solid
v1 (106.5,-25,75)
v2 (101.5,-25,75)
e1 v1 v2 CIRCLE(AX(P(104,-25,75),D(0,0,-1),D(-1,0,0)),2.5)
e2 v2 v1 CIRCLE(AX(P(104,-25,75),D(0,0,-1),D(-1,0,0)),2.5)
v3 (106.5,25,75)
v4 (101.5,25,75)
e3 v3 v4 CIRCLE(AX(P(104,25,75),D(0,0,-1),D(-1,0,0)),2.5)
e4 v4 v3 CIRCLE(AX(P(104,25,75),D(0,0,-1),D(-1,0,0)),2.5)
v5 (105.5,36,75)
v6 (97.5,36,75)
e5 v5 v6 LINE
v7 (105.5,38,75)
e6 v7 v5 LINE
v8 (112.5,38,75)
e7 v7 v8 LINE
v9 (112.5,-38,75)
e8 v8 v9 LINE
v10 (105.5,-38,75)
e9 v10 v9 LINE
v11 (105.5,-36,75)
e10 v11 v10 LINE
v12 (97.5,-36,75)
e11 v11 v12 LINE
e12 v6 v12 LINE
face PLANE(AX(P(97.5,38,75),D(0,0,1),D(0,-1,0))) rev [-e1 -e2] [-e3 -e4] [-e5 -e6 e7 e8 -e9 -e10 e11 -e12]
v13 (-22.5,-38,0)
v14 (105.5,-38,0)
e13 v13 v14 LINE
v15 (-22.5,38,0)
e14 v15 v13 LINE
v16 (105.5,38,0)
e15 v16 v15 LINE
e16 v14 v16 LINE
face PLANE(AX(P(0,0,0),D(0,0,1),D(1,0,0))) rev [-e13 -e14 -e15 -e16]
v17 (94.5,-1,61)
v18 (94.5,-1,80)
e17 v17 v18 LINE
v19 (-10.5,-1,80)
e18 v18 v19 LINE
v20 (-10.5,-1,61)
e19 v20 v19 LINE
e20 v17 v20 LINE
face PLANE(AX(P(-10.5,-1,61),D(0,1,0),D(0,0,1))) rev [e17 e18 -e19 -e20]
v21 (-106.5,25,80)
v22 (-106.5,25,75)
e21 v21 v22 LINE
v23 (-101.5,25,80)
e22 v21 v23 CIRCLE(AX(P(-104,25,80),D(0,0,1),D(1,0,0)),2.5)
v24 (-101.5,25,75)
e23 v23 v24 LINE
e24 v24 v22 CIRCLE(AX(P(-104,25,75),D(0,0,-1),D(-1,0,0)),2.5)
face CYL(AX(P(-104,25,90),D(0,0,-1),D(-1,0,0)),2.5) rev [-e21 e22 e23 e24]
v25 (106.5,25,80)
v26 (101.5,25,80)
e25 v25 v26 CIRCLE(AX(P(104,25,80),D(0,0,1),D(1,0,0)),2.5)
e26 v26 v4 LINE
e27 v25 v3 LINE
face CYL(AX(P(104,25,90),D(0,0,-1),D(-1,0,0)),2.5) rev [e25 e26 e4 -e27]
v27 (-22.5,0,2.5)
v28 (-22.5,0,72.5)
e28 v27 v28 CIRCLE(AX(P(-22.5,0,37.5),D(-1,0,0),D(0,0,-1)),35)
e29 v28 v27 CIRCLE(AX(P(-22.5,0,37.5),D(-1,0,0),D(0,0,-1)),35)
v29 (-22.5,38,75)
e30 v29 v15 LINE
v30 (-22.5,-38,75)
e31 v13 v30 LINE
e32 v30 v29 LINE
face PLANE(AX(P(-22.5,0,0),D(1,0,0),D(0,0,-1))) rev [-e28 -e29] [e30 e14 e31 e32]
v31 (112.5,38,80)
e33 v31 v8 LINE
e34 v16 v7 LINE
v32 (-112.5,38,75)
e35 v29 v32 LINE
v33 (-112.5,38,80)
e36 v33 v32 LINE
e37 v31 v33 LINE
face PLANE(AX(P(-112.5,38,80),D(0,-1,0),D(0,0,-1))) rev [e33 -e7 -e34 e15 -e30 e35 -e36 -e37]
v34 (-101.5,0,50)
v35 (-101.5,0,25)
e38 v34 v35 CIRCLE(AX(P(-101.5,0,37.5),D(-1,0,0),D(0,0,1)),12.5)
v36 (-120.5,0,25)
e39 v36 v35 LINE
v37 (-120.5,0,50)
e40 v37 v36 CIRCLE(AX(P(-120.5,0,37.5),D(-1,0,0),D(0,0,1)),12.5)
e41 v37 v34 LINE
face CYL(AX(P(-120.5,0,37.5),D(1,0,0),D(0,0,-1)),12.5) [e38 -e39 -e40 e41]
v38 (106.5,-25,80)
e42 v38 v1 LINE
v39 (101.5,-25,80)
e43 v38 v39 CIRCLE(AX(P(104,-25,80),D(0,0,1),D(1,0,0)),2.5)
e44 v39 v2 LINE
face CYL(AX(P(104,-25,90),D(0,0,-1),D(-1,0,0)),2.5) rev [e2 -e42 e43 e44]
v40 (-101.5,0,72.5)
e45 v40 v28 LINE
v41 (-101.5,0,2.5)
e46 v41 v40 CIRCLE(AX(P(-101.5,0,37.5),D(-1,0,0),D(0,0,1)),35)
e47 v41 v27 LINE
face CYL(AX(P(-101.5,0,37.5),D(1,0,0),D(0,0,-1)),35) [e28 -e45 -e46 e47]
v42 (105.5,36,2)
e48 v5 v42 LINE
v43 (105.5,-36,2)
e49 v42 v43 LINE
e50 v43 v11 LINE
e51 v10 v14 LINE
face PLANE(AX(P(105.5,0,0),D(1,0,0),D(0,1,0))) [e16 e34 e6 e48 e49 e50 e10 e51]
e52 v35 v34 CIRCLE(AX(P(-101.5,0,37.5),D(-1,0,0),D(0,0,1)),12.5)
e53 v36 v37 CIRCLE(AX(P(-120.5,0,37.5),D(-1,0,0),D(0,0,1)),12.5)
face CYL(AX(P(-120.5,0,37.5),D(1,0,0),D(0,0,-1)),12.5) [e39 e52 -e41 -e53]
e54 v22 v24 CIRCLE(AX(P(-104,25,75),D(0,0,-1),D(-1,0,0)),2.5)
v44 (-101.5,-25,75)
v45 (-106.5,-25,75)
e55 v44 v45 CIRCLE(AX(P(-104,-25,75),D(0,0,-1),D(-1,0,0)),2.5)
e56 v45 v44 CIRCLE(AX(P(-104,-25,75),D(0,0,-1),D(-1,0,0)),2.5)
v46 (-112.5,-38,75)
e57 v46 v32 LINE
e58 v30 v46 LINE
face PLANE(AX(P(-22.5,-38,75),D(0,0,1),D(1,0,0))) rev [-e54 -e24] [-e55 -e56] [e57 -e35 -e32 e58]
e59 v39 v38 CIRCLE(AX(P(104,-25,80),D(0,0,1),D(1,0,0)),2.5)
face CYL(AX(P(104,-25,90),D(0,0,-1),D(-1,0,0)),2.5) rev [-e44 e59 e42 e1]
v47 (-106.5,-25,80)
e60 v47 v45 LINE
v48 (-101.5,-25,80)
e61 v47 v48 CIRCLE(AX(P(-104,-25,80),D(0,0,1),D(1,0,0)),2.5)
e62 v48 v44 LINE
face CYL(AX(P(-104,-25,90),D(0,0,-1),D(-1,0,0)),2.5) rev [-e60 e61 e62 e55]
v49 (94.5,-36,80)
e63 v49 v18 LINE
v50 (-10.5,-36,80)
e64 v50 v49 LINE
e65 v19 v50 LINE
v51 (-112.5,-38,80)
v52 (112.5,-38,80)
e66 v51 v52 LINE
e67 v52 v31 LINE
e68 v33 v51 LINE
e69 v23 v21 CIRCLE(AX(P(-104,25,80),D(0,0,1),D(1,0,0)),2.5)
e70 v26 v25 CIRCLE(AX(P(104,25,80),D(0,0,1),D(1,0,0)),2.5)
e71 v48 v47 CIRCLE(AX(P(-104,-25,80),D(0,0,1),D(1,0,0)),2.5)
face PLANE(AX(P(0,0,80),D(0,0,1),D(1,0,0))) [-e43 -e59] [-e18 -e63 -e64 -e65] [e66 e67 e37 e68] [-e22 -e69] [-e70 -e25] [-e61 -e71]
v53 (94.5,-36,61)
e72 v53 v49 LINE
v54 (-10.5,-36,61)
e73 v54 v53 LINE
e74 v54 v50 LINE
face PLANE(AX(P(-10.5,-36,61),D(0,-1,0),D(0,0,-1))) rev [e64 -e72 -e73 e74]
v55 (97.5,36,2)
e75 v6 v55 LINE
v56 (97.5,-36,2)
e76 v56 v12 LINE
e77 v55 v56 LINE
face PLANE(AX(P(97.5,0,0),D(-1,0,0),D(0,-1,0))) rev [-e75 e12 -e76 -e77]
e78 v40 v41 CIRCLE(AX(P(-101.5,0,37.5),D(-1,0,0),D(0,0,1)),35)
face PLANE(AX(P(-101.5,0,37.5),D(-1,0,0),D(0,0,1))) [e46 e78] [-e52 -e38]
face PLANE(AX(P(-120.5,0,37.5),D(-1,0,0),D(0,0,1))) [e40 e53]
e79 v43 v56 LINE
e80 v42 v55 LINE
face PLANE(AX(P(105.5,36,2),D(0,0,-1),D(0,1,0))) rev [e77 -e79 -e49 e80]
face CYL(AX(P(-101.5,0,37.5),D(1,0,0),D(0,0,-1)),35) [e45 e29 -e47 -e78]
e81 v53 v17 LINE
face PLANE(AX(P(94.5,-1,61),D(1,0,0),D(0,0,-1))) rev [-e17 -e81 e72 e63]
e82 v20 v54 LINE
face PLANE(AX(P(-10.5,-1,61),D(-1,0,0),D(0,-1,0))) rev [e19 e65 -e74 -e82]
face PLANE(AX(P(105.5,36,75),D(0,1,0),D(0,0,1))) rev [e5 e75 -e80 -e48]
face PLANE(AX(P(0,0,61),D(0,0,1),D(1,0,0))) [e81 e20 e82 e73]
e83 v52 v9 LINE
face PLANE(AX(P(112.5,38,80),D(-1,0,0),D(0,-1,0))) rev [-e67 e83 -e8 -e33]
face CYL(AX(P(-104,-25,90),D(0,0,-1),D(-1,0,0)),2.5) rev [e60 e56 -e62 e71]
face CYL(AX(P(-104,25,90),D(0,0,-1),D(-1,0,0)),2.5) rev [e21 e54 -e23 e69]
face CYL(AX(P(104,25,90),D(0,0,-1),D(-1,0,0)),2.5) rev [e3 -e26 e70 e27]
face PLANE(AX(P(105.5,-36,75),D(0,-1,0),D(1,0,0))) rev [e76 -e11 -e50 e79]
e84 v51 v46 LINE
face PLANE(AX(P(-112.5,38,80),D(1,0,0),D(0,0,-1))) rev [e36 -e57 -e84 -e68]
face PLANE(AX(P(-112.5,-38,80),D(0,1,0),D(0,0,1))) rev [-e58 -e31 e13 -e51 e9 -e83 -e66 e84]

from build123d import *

# Parameters (mm, degrees)
SKETCH_1_W          = 225
SKETCH_1_H          = 76
EXTRUDE_1_DEPTH     = 80
SKETCH_2_W          = 75
SKETCH_2_H          = 76
CUT_EXTRUDE_1_DEPTH = 90
SKETCH_3_W          = 75
SKETCH_3_H          = 76
CUT_EXTRUDE_2_DEPTH = 15
SKETCH_4_R          = 2.5
CUT_EXTRUDE_3_DEPTH = 15
SKETCH_5_R          = 35
EXTRUDE_2_DEPTH     = 79
SKETCH_6_R          = 12.5
EXTRUDE_3_DEPTH     = 19
SKETCH_7_W          = 105
SKETCH_7_H          = 35
CUT_EXTRUDE_4_DEPTH = 19
EXTRUDE_4_DEPTH     = 8


with BuildPart() as part:
    # 草图1 → 凸台-拉伸1 (new body)
    with BuildSketch(Plane.XY):
        Rectangle(SKETCH_1_W, SKETCH_1_H)
    extrude(amount=EXTRUDE_1_DEPTH)

    # 草图2 → 切除-拉伸1 (cut)
    with BuildSketch(Plane.ZY.offset(112.5)):
        with Locations((37.5, 0)):
            Rectangle(SKETCH_2_W, SKETCH_2_H)
    extrude(amount=-CUT_EXTRUDE_1_DEPTH, mode=Mode.SUBTRACT)

    # 草图3 → 切除-拉伸2 (cut)
    with BuildSketch(Plane(origin=(112.5, 0, 0), x_dir=(0, 0, -1), z_dir=(1, 0, 0))):
        with Locations((-37.5, 0)):
            Rectangle(SKETCH_3_W, SKETCH_3_H)
    extrude(amount=-CUT_EXTRUDE_2_DEPTH, mode=Mode.SUBTRACT)

    # 草图4 → 切除-拉伸3 (cut)
    with BuildSketch(Plane(origin=(0, 0, 75), x_dir=(-1, 0, 0), z_dir=(0, 0, -1))):
        with Locations((104, -25)):
            Circle(SKETCH_4_R)
        with Locations((104, 25)):
            Circle(SKETCH_4_R)
        with Locations((-104, -25)):
            Circle(SKETCH_4_R)
        with Locations((-104, 25)):
            Circle(SKETCH_4_R)
    extrude(amount=-CUT_EXTRUDE_3_DEPTH, mode=Mode.SUBTRACT)

    # 草图5 → 凸台-拉伸2 (add)
    with BuildSketch(Plane.ZY.offset(22.5)):
        with Locations(Location((37.5, 0, 0), (0, 0, 180))):
            Circle(SKETCH_5_R)
    extrude(amount=EXTRUDE_2_DEPTH)

    # 草图6 → 凸台-拉伸3 (add)
    with BuildSketch(Plane.ZY.offset(101.5)):
        with Locations((37.5, 0)):
            Circle(SKETCH_6_R)
    extrude(amount=EXTRUDE_3_DEPTH)

    # 草图7 → 切除-拉伸4 (cut)
    with BuildSketch(Plane.XY.offset(80)):
        with Locations((42, -18.5)):
            Rectangle(SKETCH_7_W, SKETCH_7_H)
    extrude(amount=-CUT_EXTRUDE_4_DEPTH, mode=Mode.SUBTRACT)

    # 草图8 → 凸台-拉伸4 (add)
    with BuildSketch(Plane(origin=(97.5, 0, 0), x_dir=(0, 0, -1), z_dir=(1, 0, 0))):
        Polygon((-75, 38), (0, 38), (0, -38), (-75, -38), (-75, -36), (-2, -36), (-2, 36), (-75, 36), align=None)
    extrude(amount=EXTRUDE_4_DEPTH)


solid = part.part
